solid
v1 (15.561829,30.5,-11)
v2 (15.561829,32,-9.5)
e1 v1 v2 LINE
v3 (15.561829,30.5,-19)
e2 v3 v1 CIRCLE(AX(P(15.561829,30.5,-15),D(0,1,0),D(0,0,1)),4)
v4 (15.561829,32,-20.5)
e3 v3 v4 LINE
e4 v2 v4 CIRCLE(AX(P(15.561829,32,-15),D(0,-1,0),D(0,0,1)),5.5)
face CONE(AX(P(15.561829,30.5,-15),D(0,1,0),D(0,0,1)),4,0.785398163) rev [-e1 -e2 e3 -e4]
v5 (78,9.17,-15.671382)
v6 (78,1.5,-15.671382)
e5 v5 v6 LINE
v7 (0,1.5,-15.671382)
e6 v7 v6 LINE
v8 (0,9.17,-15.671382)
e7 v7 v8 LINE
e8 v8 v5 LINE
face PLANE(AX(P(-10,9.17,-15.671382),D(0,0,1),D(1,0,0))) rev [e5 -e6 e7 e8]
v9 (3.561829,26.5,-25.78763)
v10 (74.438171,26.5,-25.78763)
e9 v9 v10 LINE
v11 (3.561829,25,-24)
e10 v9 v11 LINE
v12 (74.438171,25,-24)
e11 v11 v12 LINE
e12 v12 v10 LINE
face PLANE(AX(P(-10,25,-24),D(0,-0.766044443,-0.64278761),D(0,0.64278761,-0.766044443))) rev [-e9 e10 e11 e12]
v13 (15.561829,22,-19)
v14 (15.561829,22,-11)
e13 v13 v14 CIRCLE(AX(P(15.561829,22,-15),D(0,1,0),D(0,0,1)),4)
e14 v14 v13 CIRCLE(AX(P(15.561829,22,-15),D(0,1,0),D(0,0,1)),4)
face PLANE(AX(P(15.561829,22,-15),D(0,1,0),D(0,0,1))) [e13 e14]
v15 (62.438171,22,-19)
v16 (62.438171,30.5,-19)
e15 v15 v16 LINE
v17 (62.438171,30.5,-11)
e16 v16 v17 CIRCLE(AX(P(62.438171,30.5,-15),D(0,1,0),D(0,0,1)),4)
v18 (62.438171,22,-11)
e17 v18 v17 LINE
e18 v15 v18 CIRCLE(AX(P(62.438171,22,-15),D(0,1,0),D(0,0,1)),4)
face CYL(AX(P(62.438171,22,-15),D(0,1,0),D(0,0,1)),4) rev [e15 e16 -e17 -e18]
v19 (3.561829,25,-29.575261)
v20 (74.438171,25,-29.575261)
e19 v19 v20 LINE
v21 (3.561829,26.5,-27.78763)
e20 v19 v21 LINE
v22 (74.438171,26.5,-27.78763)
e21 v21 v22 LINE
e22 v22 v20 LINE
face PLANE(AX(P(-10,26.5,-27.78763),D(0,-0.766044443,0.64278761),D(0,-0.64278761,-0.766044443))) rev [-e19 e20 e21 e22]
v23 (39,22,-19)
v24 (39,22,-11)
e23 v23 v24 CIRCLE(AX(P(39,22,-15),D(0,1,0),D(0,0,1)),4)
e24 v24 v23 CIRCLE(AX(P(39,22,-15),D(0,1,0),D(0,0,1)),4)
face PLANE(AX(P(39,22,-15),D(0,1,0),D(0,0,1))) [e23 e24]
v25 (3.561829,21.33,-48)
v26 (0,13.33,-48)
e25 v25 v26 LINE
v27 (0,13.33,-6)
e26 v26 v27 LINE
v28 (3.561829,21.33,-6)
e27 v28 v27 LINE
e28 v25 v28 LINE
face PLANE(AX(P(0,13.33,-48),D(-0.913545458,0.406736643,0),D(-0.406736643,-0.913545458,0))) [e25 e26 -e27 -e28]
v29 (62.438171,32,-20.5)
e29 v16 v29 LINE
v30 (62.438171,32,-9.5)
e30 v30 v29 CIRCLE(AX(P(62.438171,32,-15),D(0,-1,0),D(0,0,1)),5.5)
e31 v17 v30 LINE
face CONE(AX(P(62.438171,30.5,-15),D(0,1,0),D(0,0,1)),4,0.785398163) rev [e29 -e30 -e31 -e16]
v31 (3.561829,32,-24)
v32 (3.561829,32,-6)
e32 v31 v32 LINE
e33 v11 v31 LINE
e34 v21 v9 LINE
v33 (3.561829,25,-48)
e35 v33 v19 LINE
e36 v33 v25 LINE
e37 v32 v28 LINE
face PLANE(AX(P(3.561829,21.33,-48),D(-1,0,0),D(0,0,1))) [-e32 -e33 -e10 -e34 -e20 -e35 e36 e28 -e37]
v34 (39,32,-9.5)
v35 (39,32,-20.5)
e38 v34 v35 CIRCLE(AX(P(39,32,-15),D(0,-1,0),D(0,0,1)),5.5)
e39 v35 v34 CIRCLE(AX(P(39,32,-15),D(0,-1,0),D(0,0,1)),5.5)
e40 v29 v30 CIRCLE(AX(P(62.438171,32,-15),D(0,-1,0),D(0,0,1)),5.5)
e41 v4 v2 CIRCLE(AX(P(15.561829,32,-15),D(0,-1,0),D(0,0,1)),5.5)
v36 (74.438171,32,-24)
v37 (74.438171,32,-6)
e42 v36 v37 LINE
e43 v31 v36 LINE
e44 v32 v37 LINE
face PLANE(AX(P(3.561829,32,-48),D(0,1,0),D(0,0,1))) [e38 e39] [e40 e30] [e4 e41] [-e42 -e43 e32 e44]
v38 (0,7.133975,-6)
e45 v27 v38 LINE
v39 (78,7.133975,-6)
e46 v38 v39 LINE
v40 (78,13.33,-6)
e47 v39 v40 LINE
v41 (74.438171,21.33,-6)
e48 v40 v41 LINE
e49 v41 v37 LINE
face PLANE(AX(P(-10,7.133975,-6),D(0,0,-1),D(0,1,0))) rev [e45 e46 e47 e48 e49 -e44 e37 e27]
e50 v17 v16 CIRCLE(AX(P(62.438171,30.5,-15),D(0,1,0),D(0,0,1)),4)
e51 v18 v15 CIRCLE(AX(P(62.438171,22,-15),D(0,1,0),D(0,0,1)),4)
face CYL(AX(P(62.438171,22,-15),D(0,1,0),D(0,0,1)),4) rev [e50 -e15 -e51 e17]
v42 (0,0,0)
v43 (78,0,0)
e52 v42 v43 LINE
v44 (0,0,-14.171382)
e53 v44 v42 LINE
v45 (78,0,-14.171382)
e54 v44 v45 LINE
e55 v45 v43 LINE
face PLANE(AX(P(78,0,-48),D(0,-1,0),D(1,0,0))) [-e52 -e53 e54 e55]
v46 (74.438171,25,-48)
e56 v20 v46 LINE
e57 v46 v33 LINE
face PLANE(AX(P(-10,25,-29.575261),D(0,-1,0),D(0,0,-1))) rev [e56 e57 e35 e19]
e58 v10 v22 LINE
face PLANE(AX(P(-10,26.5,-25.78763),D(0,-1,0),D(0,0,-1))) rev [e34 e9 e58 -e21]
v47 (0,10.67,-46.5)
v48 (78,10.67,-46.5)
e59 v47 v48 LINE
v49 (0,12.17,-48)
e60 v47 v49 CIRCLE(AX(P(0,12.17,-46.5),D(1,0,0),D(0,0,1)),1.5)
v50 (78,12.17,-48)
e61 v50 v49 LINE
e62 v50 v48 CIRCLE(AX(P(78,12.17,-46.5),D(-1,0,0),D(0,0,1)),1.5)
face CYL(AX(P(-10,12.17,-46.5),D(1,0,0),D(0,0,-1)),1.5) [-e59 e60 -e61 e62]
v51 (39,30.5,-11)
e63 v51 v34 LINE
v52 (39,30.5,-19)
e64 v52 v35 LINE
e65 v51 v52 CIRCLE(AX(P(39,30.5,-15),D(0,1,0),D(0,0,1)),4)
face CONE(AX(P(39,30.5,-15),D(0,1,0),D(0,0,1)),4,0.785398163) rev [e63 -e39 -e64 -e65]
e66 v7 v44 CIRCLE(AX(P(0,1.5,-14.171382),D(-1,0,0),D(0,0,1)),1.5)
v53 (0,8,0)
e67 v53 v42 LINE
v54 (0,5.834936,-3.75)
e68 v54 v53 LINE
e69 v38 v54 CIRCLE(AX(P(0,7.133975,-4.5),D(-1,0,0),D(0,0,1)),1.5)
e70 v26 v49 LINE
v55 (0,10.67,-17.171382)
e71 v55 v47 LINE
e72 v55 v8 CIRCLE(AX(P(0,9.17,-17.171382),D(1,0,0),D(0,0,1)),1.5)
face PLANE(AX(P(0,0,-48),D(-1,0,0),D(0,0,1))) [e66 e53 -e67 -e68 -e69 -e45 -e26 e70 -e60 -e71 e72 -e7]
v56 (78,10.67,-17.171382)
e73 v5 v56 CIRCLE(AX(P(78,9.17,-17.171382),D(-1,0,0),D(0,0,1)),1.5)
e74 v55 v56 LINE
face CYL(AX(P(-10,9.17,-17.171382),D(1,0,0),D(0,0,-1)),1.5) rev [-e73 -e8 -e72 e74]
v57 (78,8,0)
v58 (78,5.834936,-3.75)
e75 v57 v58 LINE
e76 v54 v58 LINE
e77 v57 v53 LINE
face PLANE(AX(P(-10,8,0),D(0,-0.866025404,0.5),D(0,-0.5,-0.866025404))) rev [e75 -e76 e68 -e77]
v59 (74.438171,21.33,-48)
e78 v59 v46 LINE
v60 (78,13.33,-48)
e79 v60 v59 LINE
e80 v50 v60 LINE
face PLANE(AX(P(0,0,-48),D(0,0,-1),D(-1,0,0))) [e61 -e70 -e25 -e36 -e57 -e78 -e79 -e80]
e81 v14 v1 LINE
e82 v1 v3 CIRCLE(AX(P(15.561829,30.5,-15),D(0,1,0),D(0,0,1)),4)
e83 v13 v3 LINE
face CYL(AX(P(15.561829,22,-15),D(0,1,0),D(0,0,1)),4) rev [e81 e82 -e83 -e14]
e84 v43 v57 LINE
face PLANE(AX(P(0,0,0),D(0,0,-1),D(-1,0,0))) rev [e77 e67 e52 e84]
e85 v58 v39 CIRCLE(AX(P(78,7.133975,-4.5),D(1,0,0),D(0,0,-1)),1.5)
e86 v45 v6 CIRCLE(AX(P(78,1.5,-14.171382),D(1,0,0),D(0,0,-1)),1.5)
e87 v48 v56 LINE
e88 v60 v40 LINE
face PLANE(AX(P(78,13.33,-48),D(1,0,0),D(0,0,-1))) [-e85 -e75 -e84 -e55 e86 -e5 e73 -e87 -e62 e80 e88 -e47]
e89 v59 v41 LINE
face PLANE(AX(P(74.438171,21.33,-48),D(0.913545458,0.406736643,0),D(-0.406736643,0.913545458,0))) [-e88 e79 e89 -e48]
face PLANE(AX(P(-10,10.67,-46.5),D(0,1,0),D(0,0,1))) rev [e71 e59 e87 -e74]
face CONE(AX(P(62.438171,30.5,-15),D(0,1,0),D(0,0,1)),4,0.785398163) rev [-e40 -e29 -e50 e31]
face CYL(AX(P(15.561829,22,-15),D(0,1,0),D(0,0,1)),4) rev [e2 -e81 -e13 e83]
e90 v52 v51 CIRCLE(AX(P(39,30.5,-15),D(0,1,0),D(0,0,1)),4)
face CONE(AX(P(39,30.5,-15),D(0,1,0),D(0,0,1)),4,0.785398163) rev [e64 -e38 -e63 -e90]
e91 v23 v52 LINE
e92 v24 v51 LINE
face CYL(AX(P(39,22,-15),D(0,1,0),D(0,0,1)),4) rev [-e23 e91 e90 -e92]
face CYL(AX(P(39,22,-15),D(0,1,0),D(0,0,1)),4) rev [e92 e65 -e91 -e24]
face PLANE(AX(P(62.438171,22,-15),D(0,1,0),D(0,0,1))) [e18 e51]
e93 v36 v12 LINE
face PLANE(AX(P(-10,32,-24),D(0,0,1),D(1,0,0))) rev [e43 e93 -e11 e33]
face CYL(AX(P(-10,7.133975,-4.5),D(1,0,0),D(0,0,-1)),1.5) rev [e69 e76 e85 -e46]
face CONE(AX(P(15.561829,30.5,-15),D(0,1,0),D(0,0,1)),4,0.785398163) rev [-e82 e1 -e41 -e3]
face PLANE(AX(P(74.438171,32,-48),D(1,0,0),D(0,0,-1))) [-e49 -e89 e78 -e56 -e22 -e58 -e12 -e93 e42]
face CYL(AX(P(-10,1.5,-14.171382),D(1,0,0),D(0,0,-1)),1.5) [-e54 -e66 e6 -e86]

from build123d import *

# Parameters (mm, degrees)
DOVETAIL_BODY_DEPTH       = 48
GROOVE_CUT_DEPTH          = 88
MOUNTING_HOLES_LAYOUT_R   = 4
MOUNTING_HOLES_3X_8_DEPTH = 10
HOLE_CHAMFERS_1_5X45_SIZE = 1.5


with BuildPart() as part:
    # Dovetail Body Profile → Dovetail Body (new body)
    with BuildSketch(Plane.XY):
        Polygon((0, 0), (0, 13.33), (3.561829482, 21.33), (3.561829482, 32), (74.438170518, 32), (74.438170518, 21.33), (78, 13.33), (78, 0), align=None)
    extrude(amount=-DOVETAIL_BODY_DEPTH)

    # Groove Profile → Groove Cut (cut)
    with BuildSketch(Plane(origin=(78, 0, 0), x_dir=(0, 0, -1), z_dir=(1, 0, 0))):
        with BuildLine():
            Line((0, 8), (3.75, 5.834936491))
            ThreePointArc((3.75, 5.834936491), (5.25, 5.834936491), (6, 7.133974596))
            Line((6, 7.133974596), (6, 32))
            Line((6, 32), (0, 32))
            Line((0, 32), (0, 8))
        make_face()
        Polygon((48, 25), (48, 32), (24, 32), (24, 25), (25.787630389, 26.5), (27.787630389, 26.5), (29.575260778, 25), align=None)
        with BuildLine():
            Line((46.5, 10.67), (17.171381992, 10.67))
            ThreePointArc((17.171381992, 10.67), (16.11072182, 10.230660172), (15.671381992, 9.17))
            Line((15.671381992, 9.17), (15.671381992, 1.5))
            ThreePointArc((15.671381992, 1.5), (15.232042164, 0.439339828), (14.171381992, 0))
            Line((14.171381992, 0), (48, 0))
            Line((48, 0), (48, 12.17))
            ThreePointArc((48, 12.17), (47.560660172, 11.109339828), (46.5, 10.67))
        make_face()
    extrude(amount=-GROOVE_CUT_DEPTH, mode=Mode.SUBTRACT)

    # Mounting Holes Layout → Mounting Holes 3xØ8 (cut)
    with BuildSketch(Plane(origin=(0, 32, 0), x_dir=(1, 0, 0), z_dir=(0, 1, 0))):
        with Locations(Location((62.438170518, 15, 0), (0, 0, 270))):
            Circle(MOUNTING_HOLES_LAYOUT_R)
        with Locations(Location((39, 15, 0), (0, 0, 270))):
            Circle(MOUNTING_HOLES_LAYOUT_R)
        with Locations(Location((15.561829482, 15, 0), (0, 0, 270))):
            Circle(MOUNTING_HOLES_LAYOUT_R)
    extrude(amount=-MOUNTING_HOLES_3X_8_DEPTH, mode=Mode.SUBTRACT)

    # Hole Chamfers 1.5x45
    hole_chamfers_1_5x45_edges = [part.edges().sort_by_distance(p)[0] for p in [
        (62.438170518, 32, -19),
        (39, 32, -19),
        (15.561829482, 32, -19),
    ]]
    chamfer(hole_chamfers_1_5x45_edges, length=HOLE_CHAMFERS_1_5X45_SIZE)


solid = part.part
